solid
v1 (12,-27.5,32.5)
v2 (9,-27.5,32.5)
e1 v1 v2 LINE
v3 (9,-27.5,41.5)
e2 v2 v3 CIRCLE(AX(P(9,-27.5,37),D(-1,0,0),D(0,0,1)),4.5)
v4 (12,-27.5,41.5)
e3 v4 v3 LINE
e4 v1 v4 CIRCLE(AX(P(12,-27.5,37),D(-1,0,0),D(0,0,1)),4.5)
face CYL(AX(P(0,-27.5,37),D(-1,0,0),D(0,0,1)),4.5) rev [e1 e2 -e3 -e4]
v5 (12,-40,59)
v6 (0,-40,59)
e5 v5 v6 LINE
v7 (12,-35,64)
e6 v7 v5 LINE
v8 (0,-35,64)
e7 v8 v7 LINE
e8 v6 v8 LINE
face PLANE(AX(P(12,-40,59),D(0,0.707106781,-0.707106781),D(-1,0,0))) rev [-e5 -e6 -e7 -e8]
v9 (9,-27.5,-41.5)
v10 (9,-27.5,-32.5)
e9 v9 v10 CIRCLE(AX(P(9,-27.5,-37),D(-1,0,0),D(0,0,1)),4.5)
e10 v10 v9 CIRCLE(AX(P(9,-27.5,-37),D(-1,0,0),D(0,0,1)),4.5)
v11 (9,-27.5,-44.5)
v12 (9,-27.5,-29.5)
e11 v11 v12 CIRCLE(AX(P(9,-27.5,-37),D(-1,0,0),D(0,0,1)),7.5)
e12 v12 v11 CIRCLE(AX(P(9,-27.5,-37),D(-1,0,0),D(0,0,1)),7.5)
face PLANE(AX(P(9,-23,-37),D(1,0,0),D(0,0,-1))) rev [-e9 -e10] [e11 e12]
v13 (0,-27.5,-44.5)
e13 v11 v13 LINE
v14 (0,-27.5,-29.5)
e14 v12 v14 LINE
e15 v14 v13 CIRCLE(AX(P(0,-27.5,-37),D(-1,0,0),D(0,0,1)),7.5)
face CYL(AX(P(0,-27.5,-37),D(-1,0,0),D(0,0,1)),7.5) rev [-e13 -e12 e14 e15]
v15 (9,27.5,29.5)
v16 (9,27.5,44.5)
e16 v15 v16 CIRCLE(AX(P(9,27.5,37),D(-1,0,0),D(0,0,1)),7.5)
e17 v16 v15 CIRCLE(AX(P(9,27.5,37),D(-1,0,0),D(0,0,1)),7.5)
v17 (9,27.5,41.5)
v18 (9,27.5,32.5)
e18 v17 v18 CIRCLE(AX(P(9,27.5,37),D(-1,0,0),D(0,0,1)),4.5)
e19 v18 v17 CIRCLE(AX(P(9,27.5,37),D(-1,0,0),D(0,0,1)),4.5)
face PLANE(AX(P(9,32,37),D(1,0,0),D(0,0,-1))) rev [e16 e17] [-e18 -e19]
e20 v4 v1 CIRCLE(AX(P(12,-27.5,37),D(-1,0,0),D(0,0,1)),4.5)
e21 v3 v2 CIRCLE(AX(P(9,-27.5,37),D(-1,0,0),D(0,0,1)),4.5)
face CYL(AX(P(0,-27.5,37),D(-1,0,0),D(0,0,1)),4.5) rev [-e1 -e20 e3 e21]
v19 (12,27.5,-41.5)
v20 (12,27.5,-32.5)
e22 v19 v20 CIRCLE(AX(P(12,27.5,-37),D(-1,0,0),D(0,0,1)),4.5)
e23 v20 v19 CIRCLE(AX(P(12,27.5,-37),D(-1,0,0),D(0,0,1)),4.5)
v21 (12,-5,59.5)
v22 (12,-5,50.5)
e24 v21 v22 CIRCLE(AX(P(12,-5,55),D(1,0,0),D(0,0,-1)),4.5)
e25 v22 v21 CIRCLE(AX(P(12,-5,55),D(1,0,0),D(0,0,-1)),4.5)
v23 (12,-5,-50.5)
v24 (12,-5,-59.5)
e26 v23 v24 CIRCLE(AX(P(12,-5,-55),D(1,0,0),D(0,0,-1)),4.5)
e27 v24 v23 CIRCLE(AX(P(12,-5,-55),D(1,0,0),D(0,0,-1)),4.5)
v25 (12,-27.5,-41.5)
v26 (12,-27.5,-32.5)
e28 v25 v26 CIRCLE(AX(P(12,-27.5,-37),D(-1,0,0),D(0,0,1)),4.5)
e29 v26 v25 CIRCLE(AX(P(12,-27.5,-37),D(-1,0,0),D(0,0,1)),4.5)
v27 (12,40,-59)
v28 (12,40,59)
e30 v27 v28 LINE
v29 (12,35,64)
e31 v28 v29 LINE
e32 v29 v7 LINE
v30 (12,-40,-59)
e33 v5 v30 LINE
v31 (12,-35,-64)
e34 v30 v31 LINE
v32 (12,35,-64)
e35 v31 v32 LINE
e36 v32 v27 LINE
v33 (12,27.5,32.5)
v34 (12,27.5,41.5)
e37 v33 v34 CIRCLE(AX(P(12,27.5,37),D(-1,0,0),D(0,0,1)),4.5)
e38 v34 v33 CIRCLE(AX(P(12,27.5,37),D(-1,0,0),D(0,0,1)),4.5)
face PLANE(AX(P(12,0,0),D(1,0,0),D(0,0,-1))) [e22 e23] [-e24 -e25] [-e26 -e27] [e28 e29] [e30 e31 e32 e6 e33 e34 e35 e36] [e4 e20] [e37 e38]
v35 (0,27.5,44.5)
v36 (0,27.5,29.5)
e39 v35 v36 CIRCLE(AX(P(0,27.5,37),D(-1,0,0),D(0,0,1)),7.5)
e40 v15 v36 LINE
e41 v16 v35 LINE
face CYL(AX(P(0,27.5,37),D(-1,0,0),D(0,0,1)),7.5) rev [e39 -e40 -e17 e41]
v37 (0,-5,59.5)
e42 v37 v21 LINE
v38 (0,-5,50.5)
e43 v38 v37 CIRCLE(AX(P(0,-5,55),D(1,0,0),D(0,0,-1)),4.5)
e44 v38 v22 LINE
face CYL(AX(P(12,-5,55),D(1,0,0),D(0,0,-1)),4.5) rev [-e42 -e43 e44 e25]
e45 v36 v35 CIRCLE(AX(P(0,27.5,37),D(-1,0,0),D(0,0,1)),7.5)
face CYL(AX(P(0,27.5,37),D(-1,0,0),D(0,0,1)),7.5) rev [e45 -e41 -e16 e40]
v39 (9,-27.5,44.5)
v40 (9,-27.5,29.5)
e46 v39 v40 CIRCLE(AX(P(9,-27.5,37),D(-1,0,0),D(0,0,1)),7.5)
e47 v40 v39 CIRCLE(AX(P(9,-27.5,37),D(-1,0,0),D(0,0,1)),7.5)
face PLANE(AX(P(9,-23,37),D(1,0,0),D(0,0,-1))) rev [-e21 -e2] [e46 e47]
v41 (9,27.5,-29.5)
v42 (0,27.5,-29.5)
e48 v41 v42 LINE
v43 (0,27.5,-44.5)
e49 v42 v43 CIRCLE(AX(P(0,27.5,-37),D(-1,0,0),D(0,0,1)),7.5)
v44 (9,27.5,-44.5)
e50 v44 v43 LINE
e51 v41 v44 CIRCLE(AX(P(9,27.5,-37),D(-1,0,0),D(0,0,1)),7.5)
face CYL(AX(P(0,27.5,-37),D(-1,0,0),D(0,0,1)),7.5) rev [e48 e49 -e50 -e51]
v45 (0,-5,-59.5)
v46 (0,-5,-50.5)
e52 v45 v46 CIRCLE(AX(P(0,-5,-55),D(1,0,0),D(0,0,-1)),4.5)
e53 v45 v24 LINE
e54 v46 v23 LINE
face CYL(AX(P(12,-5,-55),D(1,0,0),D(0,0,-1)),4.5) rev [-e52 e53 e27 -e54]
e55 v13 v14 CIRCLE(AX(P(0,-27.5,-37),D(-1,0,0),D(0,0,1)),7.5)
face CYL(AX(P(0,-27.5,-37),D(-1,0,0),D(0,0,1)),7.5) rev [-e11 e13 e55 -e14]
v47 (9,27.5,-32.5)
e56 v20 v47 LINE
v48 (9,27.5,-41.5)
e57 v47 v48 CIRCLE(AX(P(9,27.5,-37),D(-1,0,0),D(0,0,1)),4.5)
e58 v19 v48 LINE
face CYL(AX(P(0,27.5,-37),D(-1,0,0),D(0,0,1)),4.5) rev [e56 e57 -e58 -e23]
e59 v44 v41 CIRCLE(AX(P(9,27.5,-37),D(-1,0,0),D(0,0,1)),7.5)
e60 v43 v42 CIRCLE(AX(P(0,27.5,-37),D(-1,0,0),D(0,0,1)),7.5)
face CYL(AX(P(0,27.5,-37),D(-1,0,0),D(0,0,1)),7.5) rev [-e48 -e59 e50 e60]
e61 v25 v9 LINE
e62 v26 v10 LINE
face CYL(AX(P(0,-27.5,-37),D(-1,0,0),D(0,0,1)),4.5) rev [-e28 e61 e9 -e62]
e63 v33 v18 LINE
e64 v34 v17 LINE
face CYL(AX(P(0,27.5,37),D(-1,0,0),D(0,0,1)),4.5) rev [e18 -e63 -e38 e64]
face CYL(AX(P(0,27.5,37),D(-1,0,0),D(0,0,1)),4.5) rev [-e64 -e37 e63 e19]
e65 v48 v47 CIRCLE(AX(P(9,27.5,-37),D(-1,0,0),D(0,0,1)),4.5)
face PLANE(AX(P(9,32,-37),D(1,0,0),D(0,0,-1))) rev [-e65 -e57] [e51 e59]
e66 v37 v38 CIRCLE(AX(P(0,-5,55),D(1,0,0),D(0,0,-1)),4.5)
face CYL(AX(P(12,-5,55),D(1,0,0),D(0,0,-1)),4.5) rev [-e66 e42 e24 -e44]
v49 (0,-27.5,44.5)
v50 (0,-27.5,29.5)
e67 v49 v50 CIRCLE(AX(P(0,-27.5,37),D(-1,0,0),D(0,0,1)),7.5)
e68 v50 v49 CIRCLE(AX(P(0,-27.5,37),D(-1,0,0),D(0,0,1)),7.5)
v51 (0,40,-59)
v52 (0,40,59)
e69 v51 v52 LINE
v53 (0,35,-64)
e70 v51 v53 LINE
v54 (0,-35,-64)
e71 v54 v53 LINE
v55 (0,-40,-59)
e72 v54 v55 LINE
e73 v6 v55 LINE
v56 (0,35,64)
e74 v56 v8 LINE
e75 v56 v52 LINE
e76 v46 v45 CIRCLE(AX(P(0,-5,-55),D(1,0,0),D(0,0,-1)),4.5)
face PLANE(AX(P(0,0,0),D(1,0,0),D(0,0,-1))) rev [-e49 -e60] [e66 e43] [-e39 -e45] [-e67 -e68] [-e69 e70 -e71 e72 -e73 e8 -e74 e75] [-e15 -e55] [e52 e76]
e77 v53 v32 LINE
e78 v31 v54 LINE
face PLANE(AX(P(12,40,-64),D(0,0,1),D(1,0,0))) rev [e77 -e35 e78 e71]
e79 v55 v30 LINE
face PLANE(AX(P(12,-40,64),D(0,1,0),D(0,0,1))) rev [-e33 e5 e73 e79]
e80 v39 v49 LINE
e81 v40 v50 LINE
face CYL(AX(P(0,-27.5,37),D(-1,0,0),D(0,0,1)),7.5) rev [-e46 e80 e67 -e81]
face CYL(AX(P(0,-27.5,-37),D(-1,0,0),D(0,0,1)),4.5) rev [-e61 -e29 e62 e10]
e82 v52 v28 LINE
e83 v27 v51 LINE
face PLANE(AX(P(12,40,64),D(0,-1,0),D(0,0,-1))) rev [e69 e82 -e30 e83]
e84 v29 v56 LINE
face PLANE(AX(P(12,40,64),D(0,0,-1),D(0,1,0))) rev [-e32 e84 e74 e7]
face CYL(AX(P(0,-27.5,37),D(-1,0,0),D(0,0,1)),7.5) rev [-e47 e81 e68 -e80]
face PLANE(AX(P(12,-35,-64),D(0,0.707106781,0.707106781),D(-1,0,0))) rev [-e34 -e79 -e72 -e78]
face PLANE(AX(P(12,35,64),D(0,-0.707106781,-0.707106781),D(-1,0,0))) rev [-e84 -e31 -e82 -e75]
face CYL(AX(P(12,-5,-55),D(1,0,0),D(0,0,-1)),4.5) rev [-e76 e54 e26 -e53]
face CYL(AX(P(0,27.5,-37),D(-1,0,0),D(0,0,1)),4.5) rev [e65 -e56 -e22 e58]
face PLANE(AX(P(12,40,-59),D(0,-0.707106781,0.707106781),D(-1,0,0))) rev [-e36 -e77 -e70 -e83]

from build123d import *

# Parameters (mm, degrees)
SKETCH_1_W                = 128
SKETCH_1_H                = 80
EXTRUDE_1_DEPTH           = 12
HOLE_WIZARD_1_D           = 9
HOLE_WIZARD_1_CBORE_D     = 15
HOLE_WIZARD_1_CBORE_DEPTH = 9
HOLE_WIZARD_9_0_9_1_D     = 9
CHAMFER_1_SIZE            = 5


with BuildPart() as part:
    # 草图1 → 凸台-拉伸1 (new body)
    with BuildSketch(Plane(origin=(0, 0, 0), x_dir=(0, 0, -1), z_dir=(1, 0, 0))):
        Rectangle(SKETCH_1_W, SKETCH_1_H)
    extrude(amount=EXTRUDE_1_DEPTH)

    # 打孔尺寸(%根据)内六角圆柱头螺钉的类型1 (through all)
    with Locations(Plane.ZY):
        with Locations((-37, 27.5), (-37, -27.5), (37, 27.5), (37, -27.5)):
            CounterBoreHole(HOLE_WIZARD_1_D / 2, HOLE_WIZARD_1_CBORE_D / 2, HOLE_WIZARD_1_CBORE_DEPTH)

    # Ø9.0 (9) 直径孔1 (through all)
    with Locations(Plane(origin=(12, 0, 0), x_dir=(0, 0, -1), z_dir=(1, 0, 0))):
        with Locations((-55, -5), (55, -5)):
            Hole(HOLE_WIZARD_9_0_9_1_D / 2)

    # 倒角1
    chamfer_1_edges = [part.edges().sort_by_distance(p)[0] for p in [
        (6, -40, -64),
        (6, -40, 64),
        (6, 40, 64),
        (6, 40, -64),
    ]]
    chamfer(chamfer_1_edges, length=CHAMFER_1_SIZE)


solid = part.part
